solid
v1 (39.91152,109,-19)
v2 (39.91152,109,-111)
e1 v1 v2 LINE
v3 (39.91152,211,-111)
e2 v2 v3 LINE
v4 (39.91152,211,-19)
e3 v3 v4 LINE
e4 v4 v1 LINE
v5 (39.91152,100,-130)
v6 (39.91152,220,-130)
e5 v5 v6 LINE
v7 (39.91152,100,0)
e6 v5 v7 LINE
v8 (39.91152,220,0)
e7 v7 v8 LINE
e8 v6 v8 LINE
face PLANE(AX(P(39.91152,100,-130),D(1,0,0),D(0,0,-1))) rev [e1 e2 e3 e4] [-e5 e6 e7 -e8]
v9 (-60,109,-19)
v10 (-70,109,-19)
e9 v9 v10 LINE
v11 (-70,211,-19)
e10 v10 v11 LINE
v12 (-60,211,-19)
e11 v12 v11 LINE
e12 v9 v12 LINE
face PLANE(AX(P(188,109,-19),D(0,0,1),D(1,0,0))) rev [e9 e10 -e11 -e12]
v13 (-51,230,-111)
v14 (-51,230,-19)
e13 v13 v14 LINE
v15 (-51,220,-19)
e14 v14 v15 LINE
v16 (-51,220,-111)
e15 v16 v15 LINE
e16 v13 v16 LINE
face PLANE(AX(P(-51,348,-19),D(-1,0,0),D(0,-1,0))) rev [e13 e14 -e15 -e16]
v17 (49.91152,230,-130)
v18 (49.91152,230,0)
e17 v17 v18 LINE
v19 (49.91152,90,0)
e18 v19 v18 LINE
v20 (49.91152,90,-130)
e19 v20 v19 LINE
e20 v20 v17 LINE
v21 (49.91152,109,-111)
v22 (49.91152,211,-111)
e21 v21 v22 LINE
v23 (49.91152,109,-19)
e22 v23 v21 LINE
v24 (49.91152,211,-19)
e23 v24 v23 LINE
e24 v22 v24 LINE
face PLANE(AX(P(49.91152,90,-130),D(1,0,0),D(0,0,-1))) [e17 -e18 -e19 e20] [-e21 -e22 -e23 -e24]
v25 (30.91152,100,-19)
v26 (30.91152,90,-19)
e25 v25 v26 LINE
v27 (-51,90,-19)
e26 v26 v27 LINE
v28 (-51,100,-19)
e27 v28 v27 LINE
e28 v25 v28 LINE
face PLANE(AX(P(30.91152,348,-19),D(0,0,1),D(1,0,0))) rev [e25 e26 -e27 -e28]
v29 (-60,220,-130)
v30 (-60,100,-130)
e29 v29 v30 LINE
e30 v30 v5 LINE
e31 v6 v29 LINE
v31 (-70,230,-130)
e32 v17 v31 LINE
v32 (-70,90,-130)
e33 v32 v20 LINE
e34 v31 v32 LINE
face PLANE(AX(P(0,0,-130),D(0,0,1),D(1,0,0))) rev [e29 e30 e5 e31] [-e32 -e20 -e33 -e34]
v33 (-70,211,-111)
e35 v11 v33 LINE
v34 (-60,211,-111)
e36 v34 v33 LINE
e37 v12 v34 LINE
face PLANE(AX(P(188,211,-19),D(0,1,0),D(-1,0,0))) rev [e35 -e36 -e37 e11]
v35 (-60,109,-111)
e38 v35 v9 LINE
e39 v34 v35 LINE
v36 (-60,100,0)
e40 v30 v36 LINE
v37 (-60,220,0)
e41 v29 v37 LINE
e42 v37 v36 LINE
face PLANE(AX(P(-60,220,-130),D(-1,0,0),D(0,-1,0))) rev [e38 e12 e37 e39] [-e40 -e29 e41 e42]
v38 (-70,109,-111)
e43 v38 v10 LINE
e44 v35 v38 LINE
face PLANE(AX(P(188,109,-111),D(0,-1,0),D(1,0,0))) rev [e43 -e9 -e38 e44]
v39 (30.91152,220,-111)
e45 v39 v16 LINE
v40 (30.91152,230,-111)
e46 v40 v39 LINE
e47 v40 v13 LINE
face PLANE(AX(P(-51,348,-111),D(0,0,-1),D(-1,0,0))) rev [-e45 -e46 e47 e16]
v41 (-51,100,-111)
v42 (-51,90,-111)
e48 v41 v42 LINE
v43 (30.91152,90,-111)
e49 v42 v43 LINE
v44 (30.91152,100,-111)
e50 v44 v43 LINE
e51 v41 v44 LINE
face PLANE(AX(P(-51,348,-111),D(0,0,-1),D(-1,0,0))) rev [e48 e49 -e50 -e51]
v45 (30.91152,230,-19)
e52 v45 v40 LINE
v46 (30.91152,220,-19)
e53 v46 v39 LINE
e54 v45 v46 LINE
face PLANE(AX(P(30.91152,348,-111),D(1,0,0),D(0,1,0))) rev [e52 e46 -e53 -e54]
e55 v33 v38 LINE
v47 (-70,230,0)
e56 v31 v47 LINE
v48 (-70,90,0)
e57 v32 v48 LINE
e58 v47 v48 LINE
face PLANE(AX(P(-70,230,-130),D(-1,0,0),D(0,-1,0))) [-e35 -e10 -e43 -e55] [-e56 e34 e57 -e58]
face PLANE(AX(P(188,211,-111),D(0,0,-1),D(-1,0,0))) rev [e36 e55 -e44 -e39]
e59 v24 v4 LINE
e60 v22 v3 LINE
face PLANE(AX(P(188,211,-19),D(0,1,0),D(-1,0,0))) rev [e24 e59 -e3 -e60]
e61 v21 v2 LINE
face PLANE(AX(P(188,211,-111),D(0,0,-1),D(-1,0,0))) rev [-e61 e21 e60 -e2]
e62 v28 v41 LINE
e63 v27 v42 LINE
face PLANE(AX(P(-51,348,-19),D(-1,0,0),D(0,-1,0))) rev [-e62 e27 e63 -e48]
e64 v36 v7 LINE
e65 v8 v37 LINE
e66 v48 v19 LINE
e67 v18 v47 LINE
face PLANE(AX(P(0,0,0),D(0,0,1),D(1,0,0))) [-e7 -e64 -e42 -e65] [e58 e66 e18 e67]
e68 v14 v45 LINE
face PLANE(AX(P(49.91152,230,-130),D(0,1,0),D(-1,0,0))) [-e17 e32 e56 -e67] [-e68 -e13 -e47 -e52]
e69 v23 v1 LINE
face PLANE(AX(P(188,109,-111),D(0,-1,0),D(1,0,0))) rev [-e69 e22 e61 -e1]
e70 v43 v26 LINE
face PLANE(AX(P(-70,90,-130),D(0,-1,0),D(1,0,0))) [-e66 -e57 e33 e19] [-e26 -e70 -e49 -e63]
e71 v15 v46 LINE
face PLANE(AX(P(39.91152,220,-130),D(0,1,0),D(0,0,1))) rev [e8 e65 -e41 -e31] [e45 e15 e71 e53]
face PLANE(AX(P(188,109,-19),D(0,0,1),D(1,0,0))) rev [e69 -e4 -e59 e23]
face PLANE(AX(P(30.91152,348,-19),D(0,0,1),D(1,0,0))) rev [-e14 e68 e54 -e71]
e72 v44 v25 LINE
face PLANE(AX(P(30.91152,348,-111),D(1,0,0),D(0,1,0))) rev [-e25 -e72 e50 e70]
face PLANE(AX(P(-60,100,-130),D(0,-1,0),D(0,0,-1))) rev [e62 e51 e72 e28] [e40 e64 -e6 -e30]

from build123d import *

# Parameters (mm, degrees)
SKETCH1_W           = 119.911519959
SKETCH1_H           = 140
SKETCH1_W_2         = 99.911519959
SKETCH1_H_2         = 120
BOSS_EXTRUDE1_DEPTH = 130
SKETCH2_W           = 81.911519959
SKETCH2_H           = 92
CUT_EXTRUDE1_DEPTH  = 258
SKETCH3_W           = 92
SKETCH3_H           = 102
CUT_EXTRUDE2_DEPTH  = 258


with BuildPart() as part:
    # Sketch1 → Boss-Extrude1 (new body)
    with BuildSketch(Plane.XY):
        with Locations((-10.04424002, 160)):
            Rectangle(SKETCH1_W, SKETCH1_H)
        with Locations((-10.044240021, 160)):
            Rectangle(SKETCH1_W_2, SKETCH1_H_2, mode=Mode.SUBTRACT)
    extrude(amount=-BOSS_EXTRUDE1_DEPTH)

    # Sketch2 → Cut-Extrude1 (cut)
    with BuildSketch(Plane.XZ.offset(-90)):
        with Locations((-10.04424002, -65)):
            Rectangle(SKETCH2_W, SKETCH2_H)
    extrude(amount=-CUT_EXTRUDE1_DEPTH, mode=Mode.SUBTRACT)

    # Sketch3 → Cut-Extrude2 (cut)
    with BuildSketch(Plane.ZY.offset(70)):
        with Locations((-65, 160)):
            Rectangle(SKETCH3_W, SKETCH3_H)
    extrude(amount=-CUT_EXTRUDE2_DEPTH, mode=Mode.SUBTRACT)


solid = part.part
